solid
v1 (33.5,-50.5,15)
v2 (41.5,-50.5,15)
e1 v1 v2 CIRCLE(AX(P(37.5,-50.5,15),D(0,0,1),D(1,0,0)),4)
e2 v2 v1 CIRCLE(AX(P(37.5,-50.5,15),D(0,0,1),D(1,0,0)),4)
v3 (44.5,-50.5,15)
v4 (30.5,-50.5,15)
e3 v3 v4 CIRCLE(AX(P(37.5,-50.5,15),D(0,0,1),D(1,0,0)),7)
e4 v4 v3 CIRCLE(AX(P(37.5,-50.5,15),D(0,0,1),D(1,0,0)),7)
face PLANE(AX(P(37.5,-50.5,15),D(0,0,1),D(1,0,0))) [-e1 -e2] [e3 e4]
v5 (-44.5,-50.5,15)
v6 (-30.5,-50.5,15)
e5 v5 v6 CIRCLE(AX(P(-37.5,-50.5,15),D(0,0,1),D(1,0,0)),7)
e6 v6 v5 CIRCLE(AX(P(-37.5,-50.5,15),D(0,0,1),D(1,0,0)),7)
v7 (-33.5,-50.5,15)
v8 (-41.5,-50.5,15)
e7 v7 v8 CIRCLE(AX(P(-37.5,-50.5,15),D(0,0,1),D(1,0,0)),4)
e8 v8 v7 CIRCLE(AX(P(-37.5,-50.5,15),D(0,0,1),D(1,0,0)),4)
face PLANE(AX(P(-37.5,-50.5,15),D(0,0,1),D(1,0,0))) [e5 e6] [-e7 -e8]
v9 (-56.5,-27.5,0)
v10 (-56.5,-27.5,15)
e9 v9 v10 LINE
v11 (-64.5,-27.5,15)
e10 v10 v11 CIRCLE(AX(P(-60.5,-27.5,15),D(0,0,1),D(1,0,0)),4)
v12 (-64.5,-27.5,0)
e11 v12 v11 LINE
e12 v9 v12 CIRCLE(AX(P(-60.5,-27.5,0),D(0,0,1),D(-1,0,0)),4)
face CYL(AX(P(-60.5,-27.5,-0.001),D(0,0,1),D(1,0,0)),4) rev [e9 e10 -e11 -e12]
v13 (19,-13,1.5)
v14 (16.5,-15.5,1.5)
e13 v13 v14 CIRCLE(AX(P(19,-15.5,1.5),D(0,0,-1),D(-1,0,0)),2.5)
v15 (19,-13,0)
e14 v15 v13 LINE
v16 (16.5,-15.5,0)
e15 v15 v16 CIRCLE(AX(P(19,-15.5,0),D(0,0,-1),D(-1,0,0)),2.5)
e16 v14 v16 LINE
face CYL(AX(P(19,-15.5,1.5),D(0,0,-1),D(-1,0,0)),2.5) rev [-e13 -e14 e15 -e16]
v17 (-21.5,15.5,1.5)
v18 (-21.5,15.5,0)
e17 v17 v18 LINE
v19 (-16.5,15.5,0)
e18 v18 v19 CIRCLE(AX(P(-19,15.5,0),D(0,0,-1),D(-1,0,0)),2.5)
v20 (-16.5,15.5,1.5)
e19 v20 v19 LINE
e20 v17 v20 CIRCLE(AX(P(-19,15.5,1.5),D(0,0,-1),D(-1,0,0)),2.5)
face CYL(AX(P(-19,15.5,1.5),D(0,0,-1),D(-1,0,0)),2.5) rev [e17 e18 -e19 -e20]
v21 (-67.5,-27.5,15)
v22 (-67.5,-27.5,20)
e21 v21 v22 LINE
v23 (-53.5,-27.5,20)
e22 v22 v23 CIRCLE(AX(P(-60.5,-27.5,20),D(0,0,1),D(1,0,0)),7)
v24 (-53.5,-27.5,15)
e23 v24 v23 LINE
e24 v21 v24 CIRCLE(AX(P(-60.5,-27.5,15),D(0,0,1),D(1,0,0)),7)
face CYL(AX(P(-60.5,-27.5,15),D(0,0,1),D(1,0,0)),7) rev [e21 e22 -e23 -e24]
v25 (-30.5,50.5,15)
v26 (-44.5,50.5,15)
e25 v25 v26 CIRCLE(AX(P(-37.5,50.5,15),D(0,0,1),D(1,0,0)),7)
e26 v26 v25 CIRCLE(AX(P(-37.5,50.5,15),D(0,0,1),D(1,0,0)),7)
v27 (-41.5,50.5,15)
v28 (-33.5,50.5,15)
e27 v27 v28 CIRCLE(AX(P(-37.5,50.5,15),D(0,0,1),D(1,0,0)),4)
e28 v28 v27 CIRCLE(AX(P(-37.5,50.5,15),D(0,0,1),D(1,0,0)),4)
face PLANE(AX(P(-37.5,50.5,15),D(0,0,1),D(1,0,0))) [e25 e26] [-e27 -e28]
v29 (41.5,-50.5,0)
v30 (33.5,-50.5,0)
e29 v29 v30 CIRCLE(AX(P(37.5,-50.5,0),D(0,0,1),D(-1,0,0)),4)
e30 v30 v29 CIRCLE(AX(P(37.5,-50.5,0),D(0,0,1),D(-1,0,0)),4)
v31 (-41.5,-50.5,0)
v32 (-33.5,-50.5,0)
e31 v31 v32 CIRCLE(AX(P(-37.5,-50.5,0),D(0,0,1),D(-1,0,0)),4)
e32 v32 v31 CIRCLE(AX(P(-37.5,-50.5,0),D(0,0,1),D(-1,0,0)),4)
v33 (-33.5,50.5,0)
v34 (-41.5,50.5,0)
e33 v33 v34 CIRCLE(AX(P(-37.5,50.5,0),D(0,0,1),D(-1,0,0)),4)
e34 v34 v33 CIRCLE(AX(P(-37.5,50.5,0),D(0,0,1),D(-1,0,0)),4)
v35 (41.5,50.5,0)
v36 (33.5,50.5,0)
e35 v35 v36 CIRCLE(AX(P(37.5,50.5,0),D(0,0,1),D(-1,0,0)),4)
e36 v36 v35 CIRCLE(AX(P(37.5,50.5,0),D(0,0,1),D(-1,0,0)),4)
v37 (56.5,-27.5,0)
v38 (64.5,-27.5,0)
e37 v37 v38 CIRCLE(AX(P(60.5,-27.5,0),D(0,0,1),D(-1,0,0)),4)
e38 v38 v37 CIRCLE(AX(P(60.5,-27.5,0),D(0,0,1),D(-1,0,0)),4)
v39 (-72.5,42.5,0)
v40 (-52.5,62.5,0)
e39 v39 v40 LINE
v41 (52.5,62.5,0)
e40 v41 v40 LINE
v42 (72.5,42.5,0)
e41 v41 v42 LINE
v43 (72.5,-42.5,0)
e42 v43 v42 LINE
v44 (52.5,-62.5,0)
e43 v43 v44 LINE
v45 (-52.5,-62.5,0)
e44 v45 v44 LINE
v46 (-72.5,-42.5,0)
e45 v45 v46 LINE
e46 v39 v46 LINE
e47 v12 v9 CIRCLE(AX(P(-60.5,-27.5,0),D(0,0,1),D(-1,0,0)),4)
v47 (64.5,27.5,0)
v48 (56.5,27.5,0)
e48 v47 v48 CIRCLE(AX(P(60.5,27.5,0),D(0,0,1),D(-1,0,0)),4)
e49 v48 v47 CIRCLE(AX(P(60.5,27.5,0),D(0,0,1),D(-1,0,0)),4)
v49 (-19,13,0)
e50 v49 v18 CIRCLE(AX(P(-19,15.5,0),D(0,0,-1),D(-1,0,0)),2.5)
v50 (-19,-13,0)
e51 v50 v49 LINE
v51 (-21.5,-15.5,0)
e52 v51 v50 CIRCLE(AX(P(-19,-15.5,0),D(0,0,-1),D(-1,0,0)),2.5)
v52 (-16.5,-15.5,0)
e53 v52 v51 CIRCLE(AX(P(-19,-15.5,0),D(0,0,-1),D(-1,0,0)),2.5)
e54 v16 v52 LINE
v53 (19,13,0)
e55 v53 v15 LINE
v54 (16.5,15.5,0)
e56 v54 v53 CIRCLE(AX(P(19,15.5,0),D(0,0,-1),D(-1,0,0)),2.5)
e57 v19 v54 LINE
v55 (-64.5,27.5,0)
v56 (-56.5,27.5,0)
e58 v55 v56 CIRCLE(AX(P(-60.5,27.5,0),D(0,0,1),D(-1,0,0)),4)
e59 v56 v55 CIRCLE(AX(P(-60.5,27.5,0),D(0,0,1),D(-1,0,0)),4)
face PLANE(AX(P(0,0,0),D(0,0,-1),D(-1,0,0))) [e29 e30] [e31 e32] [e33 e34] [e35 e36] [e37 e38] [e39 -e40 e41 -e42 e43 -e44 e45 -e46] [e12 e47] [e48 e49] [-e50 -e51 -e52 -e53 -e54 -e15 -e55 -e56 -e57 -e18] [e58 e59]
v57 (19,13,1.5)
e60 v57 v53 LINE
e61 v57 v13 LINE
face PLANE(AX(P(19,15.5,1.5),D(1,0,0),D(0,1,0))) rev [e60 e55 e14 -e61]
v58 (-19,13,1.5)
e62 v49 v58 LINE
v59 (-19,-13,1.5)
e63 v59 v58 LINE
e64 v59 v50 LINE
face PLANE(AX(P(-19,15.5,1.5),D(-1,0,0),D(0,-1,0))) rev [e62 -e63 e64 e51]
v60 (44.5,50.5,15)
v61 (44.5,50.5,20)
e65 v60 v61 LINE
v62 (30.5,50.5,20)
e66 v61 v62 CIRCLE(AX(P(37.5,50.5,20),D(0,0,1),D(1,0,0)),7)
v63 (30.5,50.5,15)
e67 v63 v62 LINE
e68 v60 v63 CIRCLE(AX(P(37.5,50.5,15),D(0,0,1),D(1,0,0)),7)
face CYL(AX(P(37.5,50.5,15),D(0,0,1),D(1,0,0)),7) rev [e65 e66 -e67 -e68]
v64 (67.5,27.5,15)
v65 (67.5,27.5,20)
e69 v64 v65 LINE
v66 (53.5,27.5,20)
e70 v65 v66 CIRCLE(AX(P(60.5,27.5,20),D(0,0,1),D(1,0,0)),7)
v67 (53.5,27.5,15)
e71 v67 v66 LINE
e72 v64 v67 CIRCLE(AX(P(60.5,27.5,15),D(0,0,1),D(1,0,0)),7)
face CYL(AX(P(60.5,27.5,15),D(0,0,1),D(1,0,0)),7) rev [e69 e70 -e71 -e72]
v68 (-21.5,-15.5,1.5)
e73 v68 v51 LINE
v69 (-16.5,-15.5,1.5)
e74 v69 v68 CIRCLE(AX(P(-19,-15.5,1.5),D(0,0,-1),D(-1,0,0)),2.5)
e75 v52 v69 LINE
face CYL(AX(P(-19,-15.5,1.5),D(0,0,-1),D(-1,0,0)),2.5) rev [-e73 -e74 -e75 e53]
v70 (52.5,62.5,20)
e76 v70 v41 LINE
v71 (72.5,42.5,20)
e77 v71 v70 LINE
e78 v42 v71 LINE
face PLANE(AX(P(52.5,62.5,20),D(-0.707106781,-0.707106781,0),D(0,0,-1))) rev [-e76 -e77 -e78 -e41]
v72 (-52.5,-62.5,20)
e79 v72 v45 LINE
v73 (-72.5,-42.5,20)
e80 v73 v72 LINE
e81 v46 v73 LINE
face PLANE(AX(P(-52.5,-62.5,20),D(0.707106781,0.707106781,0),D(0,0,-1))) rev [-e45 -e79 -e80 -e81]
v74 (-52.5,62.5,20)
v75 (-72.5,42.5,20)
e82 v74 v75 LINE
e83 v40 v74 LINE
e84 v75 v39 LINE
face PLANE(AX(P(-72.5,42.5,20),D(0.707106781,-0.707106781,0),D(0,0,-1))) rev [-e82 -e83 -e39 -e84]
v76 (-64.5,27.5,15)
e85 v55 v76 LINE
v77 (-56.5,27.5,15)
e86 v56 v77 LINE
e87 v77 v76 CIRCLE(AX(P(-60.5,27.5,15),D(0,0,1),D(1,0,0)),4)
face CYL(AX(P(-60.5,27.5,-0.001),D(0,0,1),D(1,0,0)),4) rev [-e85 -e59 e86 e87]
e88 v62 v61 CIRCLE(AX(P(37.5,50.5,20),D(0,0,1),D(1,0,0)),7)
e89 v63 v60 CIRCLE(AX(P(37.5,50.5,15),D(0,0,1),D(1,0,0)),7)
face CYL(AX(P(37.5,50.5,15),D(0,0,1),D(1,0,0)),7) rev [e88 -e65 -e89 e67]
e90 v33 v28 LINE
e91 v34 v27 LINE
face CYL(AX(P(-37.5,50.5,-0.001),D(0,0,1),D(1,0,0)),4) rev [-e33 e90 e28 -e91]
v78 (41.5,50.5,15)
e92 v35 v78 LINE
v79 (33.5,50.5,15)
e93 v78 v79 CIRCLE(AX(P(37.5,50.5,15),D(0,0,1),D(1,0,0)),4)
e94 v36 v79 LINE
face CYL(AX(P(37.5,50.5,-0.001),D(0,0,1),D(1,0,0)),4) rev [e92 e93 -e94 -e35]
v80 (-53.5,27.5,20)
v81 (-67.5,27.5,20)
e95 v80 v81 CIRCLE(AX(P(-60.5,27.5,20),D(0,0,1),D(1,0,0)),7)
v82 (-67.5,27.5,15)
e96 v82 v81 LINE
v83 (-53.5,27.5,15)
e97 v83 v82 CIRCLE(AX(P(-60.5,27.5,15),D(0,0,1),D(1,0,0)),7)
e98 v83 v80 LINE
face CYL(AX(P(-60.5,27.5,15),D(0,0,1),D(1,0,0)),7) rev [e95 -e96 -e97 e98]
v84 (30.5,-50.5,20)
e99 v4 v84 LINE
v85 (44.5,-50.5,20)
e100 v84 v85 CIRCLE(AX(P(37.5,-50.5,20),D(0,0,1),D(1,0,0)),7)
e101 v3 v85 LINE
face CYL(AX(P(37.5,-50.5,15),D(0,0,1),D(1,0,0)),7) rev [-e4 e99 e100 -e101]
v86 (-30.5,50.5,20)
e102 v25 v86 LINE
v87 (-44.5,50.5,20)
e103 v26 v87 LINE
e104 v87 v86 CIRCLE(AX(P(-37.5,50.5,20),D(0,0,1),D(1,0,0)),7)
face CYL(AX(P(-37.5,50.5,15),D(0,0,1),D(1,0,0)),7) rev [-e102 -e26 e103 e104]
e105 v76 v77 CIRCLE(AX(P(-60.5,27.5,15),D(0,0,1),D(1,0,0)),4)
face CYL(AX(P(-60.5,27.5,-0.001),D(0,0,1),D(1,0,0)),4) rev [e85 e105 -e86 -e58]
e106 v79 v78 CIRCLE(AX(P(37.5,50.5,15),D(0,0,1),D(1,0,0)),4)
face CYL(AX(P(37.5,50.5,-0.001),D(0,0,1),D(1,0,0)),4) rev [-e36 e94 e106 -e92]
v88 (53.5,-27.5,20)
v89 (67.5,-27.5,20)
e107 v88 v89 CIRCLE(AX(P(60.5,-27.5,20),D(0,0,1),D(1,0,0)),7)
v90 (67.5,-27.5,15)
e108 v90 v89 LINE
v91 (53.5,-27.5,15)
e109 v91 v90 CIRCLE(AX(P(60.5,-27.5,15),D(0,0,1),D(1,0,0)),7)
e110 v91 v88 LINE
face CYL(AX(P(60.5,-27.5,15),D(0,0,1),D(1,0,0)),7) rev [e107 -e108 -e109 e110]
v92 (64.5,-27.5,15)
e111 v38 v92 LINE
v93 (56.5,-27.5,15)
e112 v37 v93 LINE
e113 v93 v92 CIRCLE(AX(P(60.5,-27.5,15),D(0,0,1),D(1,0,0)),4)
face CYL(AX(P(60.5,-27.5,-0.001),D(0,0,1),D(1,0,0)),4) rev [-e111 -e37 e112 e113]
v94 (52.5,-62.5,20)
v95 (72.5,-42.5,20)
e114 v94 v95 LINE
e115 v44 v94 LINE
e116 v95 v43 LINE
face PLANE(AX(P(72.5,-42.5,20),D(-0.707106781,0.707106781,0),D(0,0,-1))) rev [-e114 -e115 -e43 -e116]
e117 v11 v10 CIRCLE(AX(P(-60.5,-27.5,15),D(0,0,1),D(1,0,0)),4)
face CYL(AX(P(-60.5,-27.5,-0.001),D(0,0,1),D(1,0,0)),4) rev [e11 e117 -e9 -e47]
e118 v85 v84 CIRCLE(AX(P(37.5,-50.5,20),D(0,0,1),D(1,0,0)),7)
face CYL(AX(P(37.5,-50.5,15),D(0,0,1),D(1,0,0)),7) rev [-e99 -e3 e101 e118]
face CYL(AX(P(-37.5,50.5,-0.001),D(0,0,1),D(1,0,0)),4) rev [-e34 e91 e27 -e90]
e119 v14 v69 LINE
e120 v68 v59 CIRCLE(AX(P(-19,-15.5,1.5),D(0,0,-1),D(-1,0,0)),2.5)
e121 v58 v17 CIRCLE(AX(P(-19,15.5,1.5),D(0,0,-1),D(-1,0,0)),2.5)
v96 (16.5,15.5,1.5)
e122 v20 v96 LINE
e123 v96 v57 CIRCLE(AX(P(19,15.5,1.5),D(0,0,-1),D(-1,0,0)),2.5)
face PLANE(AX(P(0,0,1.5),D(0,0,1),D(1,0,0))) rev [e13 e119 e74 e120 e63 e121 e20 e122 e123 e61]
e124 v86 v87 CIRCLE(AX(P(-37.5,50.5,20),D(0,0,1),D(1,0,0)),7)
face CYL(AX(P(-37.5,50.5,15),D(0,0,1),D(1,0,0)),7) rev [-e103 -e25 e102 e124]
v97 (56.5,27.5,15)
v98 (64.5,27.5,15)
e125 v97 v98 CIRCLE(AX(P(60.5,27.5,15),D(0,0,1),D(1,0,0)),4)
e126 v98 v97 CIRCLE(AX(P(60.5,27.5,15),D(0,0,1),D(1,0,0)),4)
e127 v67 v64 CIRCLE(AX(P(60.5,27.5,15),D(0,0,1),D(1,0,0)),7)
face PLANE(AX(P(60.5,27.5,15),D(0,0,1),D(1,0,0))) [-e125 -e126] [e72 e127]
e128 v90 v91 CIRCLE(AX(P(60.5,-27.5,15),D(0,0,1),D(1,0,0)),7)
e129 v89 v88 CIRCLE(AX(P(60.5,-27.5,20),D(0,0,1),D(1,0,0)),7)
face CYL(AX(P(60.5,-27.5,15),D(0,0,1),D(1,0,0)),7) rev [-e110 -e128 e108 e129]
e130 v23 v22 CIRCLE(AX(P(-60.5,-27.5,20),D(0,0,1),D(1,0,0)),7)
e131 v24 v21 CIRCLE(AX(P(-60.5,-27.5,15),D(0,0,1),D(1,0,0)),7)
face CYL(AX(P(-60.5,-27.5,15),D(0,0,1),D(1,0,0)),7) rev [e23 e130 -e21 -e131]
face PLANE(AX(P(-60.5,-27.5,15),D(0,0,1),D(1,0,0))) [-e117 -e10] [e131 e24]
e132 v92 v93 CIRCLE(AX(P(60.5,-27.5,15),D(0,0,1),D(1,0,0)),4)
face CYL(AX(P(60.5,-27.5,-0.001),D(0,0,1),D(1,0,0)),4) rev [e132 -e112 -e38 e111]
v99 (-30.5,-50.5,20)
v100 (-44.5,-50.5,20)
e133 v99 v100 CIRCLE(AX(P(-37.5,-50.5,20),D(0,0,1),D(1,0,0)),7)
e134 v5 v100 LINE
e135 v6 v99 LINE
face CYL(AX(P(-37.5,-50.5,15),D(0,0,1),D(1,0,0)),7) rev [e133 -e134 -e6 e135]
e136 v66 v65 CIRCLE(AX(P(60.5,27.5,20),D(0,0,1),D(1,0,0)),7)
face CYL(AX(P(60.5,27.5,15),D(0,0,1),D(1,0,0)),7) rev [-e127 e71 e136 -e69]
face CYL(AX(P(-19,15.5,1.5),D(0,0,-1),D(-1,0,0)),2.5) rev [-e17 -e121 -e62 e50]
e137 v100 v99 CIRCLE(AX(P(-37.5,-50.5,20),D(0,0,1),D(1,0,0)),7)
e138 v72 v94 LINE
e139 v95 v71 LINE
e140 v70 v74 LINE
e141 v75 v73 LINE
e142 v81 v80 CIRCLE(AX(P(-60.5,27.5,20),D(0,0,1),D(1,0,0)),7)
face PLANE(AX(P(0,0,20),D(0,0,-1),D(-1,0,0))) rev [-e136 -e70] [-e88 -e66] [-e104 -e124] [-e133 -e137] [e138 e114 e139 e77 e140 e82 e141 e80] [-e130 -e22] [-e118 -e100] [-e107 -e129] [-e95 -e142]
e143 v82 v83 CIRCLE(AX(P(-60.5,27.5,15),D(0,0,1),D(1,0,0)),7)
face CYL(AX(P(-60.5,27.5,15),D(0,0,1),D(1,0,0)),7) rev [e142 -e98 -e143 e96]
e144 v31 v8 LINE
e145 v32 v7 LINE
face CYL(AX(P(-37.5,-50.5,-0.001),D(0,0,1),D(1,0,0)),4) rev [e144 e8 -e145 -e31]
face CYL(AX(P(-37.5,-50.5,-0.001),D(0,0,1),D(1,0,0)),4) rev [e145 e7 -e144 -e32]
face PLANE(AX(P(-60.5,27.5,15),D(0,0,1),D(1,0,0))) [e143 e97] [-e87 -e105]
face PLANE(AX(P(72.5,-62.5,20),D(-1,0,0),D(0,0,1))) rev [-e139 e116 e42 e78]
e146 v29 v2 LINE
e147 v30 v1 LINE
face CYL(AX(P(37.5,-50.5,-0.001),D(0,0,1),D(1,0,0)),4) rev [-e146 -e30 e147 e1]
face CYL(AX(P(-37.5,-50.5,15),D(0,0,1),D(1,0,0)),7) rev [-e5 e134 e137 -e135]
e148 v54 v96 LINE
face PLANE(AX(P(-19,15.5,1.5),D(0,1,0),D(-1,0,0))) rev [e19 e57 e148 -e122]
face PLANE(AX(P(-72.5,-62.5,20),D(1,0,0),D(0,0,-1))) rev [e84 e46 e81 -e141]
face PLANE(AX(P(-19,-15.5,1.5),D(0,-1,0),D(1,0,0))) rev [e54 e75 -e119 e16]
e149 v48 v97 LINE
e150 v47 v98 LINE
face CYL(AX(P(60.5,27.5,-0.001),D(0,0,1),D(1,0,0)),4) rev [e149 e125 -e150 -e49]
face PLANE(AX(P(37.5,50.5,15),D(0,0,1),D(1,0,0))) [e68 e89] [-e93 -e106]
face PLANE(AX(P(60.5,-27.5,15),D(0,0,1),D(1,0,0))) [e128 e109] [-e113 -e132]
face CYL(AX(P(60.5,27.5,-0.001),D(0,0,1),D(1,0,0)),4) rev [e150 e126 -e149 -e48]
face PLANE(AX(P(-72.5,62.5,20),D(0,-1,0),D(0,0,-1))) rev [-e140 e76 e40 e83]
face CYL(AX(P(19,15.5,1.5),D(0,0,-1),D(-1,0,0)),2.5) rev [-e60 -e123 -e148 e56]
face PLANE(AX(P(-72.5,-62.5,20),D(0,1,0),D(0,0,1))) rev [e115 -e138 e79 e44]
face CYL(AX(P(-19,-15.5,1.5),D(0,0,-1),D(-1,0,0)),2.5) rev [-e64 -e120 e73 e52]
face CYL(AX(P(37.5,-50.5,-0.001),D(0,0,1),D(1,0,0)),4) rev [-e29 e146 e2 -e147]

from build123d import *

# Parameters (mm, degrees)
SKETCH_1_W          = 145
SKETCH_1_H          = 125
EXTRUDE_1_DEPTH     = 20
CHAMFER_1_SIZE      = 20
SKETCH_2_R          = 7
CUT_EXTRUDE_1_DEPTH = 5
CUT_EXTRUDE_2_REACH = 98.889
SKETCH_3_R          = 4
SKETCH_4_W          = 38
SKETCH_4_H          = 31
CUT_EXTRUDE_3_DEPTH = 1.5
SKETCH_5_R          = 2.5
CUT_EXTRUDE_4_DEPTH = 1.5


with BuildPart() as part:
    # 草图1 → 凸台-拉伸1 (new body)
    with BuildSketch(Plane.XY):
        Rectangle(SKETCH_1_W, SKETCH_1_H)
    extrude(amount=EXTRUDE_1_DEPTH)

    # 倒角1
    chamfer_1_edges = [part.edges().sort_by_distance(p)[0] for p in [
        (72.5, -62.5, 10),
        (-72.5, -62.5, 10),
        (-72.5, 62.5, 10),
        (72.5, 62.5, 10),
    ]]
    chamfer(chamfer_1_edges, length=CHAMFER_1_SIZE)

    # 草图2 → 切除-拉伸1 (cut)
    with BuildSketch(Plane.XY.offset(20)):
        with Locations((-37.5, 50.5)):
            Circle(SKETCH_2_R)
        with Locations((37.5, 50.5)):
            Circle(SKETCH_2_R)
        with Locations((-60.5, 27.5)):
            Circle(SKETCH_2_R)
        with Locations((-60.5, -27.5)):
            Circle(SKETCH_2_R)
        with Locations((-37.5, -50.5)):
            Circle(SKETCH_2_R)
        with Locations((37.5, -50.5)):
            Circle(SKETCH_2_R)
        with Locations((60.5, 27.5)):
            Circle(SKETCH_2_R)
        with Locations((60.5, -27.5)):
            Circle(SKETCH_2_R)
    extrude(amount=-CUT_EXTRUDE_1_DEPTH, mode=Mode.SUBTRACT)

    # 草图3 → 切除-拉伸2 (cut, up to next)
    with BuildSketch(Plane.XY.offset(15), mode=Mode.PRIVATE) as cut_extrude_2_sk1:
        with Locations((-37.5, 50.5)):
            Circle(SKETCH_3_R)
    cut_extrude_2_tool1 = extrude(cut_extrude_2_sk1.sketch, amount=-CUT_EXTRUDE_2_REACH, mode=Mode.PRIVATE) & part.part
    # 草图3 → 切除-拉伸2 (cut, up to next)
    with BuildSketch(Plane.XY.offset(15), mode=Mode.PRIVATE) as cut_extrude_2_sk2:
        with Locations((-60.5, 27.5)):
            Circle(SKETCH_3_R)
    cut_extrude_2_tool2 = extrude(cut_extrude_2_sk2.sketch, amount=-CUT_EXTRUDE_2_REACH, mode=Mode.PRIVATE) & part.part
    # 草图3 → 切除-拉伸2 (cut, up to next)
    with BuildSketch(Plane.XY.offset(15), mode=Mode.PRIVATE) as cut_extrude_2_sk3:
        with Locations((-60.5, -27.5)):
            Circle(SKETCH_3_R)
    cut_extrude_2_tool3 = extrude(cut_extrude_2_sk3.sketch, amount=-CUT_EXTRUDE_2_REACH, mode=Mode.PRIVATE) & part.part
    # 草图3 → 切除-拉伸2 (cut, up to next)
    with BuildSketch(Plane.XY.offset(15), mode=Mode.PRIVATE) as cut_extrude_2_sk4:
        with Locations((-37.5, -50.5)):
            Circle(SKETCH_3_R)
    cut_extrude_2_tool4 = extrude(cut_extrude_2_sk4.sketch, amount=-CUT_EXTRUDE_2_REACH, mode=Mode.PRIVATE) & part.part
    # 草图3 → 切除-拉伸2 (cut, up to next)
    with BuildSketch(Plane.XY.offset(15), mode=Mode.PRIVATE) as cut_extrude_2_sk5:
        with Locations((37.5, 50.5)):
            Circle(SKETCH_3_R)
    cut_extrude_2_tool5 = extrude(cut_extrude_2_sk5.sketch, amount=-CUT_EXTRUDE_2_REACH, mode=Mode.PRIVATE) & part.part
    # 草图3 → 切除-拉伸2 (cut, up to next)
    with BuildSketch(Plane.XY.offset(15), mode=Mode.PRIVATE) as cut_extrude_2_sk6:
        with Locations((60.5, 27.5)):
            Circle(SKETCH_3_R)
    cut_extrude_2_tool6 = extrude(cut_extrude_2_sk6.sketch, amount=-CUT_EXTRUDE_2_REACH, mode=Mode.PRIVATE) & part.part
    # 草图3 → 切除-拉伸2 (cut, up to next)
    with BuildSketch(Plane.XY.offset(15), mode=Mode.PRIVATE) as cut_extrude_2_sk7:
        with Locations((60.5, -27.5)):
            Circle(SKETCH_3_R)
    cut_extrude_2_tool7 = extrude(cut_extrude_2_sk7.sketch, amount=-CUT_EXTRUDE_2_REACH, mode=Mode.PRIVATE) & part.part
    # 草图3 → 切除-拉伸2 (cut, up to next)
    with BuildSketch(Plane.XY.offset(15), mode=Mode.PRIVATE) as cut_extrude_2_sk8:
        with Locations((37.5, -50.5)):
            Circle(SKETCH_3_R)
    cut_extrude_2_tool8 = extrude(cut_extrude_2_sk8.sketch, amount=-CUT_EXTRUDE_2_REACH, mode=Mode.PRIVATE) & part.part
    add(cut_extrude_2_tool1.solids().sort_by_distance((-37.5, 50.5, 15))[0], mode=Mode.SUBTRACT)
    add(cut_extrude_2_tool2.solids().sort_by_distance((-60.5, 27.5, 15))[0], mode=Mode.SUBTRACT)
    add(cut_extrude_2_tool3.solids().sort_by_distance((-60.5, -27.5, 15))[0], mode=Mode.SUBTRACT)
    add(cut_extrude_2_tool4.solids().sort_by_distance((-37.5, -50.5, 15))[0], mode=Mode.SUBTRACT)
    add(cut_extrude_2_tool5.solids().sort_by_distance((37.5, 50.5, 15))[0], mode=Mode.SUBTRACT)
    add(cut_extrude_2_tool6.solids().sort_by_distance((60.5, 27.5, 15))[0], mode=Mode.SUBTRACT)
    add(cut_extrude_2_tool7.solids().sort_by_distance((60.5, -27.5, 15))[0], mode=Mode.SUBTRACT)
    add(cut_extrude_2_tool8.solids().sort_by_distance((37.5, -50.5, 15))[0], mode=Mode.SUBTRACT)

    # 草图4 → 切除-拉伸3 (cut)
    with BuildSketch(Plane(origin=(0, 0, 0), x_dir=(-1, 0, 0), z_dir=(0, 0, -1))):
        Rectangle(SKETCH_4_W, SKETCH_4_H)
    extrude(amount=-CUT_EXTRUDE_3_DEPTH, mode=Mode.SUBTRACT)

    # 草图5 → 切除-拉伸4 (cut)
    with BuildSketch(Plane(origin=(0, 0, 0), x_dir=(-1, 0, 0), z_dir=(0, 0, -1))):
        with Locations((19, -15.5)):
            Circle(SKETCH_5_R)
        with Locations((-19, -15.5)):
            Circle(SKETCH_5_R)
        with Locations((-19, 15.5)):
            Circle(SKETCH_5_R)
        with Locations((19, 15.5)):
            Circle(SKETCH_5_R)
    extrude(amount=-CUT_EXTRUDE_4_DEPTH, mode=Mode.SUBTRACT)


solid = part.part
